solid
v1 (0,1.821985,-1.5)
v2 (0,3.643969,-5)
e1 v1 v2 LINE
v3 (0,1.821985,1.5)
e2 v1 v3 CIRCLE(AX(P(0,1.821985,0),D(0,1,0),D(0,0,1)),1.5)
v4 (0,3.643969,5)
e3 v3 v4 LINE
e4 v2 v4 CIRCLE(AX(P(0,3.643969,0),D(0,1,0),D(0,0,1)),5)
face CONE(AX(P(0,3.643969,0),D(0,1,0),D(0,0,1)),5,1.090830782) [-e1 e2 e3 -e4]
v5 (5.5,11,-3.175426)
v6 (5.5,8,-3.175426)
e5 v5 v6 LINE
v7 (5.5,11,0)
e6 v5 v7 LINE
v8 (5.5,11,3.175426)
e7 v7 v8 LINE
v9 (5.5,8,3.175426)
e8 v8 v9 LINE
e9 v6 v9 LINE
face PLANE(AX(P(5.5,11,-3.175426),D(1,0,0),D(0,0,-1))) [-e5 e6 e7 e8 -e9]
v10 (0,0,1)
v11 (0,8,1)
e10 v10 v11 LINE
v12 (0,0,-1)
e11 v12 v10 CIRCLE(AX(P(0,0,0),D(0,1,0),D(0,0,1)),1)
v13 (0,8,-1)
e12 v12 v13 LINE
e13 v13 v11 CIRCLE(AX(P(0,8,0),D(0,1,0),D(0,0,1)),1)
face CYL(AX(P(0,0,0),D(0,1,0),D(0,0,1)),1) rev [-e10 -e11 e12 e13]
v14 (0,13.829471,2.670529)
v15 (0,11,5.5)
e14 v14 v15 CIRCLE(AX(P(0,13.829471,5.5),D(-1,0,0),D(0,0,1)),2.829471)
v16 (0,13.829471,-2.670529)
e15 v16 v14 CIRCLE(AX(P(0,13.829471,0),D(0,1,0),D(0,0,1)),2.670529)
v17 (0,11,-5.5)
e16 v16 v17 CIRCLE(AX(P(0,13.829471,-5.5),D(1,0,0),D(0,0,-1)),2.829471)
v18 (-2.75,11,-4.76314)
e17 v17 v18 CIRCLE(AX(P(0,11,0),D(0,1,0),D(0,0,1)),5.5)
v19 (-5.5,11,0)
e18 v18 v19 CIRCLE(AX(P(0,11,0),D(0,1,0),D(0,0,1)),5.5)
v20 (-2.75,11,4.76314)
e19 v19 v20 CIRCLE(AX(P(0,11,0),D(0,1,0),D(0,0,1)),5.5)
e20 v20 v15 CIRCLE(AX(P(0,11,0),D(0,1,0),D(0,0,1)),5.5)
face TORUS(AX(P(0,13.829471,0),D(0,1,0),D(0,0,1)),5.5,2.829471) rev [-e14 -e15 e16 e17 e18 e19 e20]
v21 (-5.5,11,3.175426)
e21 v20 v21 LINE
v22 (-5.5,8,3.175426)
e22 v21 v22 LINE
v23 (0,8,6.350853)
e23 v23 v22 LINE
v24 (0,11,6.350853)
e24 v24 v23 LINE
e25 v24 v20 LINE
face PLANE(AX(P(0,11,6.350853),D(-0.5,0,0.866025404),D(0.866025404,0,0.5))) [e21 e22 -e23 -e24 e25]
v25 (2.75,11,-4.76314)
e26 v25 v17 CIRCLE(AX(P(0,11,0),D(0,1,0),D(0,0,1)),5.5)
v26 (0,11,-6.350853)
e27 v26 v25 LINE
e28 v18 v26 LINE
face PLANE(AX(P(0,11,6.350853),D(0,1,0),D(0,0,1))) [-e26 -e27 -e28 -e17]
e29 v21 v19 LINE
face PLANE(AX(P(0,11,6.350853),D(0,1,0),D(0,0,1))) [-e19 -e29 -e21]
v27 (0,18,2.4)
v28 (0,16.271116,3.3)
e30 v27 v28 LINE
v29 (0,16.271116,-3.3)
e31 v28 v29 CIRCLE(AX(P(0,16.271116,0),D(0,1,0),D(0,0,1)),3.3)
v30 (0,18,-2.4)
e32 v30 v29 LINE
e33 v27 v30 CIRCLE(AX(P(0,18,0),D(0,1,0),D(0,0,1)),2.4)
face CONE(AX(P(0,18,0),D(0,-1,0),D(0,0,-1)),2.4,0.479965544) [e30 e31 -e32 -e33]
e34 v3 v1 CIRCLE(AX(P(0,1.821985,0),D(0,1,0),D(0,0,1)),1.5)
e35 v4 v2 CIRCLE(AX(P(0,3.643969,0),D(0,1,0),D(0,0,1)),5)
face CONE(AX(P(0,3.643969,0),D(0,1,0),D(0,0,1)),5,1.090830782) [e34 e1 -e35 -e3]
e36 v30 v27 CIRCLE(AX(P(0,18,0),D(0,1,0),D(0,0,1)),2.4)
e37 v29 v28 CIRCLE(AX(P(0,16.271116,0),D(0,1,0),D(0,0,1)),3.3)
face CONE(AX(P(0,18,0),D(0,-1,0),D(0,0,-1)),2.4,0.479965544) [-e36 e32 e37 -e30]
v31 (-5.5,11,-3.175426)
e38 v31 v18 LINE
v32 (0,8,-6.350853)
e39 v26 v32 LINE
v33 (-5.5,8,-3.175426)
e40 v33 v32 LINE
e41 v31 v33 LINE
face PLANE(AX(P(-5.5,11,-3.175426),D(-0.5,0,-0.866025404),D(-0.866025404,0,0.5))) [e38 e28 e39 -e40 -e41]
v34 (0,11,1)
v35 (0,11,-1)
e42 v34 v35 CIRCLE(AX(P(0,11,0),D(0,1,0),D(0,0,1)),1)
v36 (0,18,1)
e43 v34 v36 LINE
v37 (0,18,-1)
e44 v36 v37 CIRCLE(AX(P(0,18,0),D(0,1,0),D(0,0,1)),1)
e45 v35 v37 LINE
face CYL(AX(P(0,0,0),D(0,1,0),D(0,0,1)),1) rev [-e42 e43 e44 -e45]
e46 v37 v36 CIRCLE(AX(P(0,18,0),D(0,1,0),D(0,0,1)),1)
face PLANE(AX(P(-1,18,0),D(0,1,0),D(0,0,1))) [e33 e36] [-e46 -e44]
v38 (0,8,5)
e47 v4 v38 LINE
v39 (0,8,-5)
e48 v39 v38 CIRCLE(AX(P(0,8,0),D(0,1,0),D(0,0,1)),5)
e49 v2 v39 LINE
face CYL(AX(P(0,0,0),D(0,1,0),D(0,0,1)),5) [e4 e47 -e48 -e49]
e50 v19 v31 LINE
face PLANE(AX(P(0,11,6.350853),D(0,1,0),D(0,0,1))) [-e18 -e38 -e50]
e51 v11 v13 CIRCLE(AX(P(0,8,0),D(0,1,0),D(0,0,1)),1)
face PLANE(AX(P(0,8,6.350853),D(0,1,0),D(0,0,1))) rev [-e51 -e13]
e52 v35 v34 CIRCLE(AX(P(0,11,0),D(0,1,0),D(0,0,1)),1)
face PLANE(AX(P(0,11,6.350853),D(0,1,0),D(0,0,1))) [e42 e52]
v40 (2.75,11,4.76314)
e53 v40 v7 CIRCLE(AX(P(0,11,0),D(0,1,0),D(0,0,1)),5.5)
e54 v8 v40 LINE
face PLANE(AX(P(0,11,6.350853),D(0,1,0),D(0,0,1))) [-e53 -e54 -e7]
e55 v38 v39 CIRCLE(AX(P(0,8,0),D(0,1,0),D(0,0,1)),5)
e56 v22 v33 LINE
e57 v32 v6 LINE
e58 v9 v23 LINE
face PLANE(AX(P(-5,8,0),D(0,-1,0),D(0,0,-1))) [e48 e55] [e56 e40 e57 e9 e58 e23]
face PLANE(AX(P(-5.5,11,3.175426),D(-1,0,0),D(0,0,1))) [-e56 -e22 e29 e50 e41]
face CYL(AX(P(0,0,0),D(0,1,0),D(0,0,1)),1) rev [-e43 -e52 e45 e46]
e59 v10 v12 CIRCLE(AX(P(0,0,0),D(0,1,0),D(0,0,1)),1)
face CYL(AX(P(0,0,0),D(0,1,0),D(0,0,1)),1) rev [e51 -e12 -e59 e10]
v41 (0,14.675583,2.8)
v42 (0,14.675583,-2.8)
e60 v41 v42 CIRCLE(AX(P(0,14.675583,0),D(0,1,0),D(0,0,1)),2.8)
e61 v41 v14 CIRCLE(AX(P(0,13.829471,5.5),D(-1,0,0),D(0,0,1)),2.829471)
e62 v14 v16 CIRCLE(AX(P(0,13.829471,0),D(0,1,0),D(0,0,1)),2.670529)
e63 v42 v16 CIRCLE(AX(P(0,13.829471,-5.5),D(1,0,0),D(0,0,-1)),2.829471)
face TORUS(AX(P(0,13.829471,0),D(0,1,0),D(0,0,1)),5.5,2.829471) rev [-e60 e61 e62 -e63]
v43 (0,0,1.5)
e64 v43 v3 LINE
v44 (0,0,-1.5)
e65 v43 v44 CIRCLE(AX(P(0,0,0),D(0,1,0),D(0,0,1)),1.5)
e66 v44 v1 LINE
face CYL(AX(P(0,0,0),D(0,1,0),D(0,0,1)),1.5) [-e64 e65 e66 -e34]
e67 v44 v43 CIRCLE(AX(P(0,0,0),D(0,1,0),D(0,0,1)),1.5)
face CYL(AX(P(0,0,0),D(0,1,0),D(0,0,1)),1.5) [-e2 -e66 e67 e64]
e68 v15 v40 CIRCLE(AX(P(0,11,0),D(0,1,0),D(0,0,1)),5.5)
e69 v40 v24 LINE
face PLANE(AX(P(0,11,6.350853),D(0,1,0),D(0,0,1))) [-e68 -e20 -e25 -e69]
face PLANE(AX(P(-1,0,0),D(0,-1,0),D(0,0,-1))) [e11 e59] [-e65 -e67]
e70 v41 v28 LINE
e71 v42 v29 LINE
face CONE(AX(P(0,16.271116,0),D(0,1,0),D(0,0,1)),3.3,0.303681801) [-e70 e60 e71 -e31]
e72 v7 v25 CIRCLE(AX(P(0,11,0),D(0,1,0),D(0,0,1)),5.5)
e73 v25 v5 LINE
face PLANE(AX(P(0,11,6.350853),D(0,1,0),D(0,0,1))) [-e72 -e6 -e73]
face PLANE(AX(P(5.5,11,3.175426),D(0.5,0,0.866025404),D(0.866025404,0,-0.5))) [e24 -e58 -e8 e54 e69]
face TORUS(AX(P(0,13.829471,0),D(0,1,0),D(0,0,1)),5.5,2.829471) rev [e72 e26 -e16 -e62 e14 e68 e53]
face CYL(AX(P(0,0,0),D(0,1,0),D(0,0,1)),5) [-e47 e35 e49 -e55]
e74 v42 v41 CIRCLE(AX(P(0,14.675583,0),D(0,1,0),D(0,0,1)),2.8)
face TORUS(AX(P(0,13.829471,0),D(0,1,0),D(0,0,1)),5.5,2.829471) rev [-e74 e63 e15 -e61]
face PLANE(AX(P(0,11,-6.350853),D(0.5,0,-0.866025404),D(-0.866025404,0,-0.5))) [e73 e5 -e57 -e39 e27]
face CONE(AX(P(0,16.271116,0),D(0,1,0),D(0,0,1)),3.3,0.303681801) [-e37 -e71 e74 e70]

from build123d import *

# Parameters (mm, degrees)
EXTRUDE_1_DEPTH = 3


with BuildPart() as part:
    # 草图1 → 旋转2 (revolve)
    with BuildSketch(Plane.XY, mode=Mode.PRIVATE) as revolve_2_sk:
        with BuildLine():
            Line((-1, 18), (-2.4, 18))
            Line((-2.4, 18), (-3.3, 16.271116086))
            Line((-3.3, 16.271116086), (-2.8, 14.675583457))
            ThreePointArc((-2.8, 14.675583457), (-3.219653878, 12.154380629), (-5.5, 11))
            Line((-5.5, 11), (-5.5, 8))
            Line((-5.5, 8), (-5, 8))
            Line((-5, 8), (-5, 3.643969354))
            Line((-5, 3.643969354), (-1.5, 1.821984677))
            Line((-1.5, 1.821984677), (-1.5, 0))
            Line((-1.5, 0), (-1, 0))
            Line((-1, 0), (-1, 18))
        make_face()
    revolve(revolve_2_sk.sketch.rotate(Axis((0, 0, 0), (0, -1, 0)), 270), axis=Axis((0, 0, 0), (0, -1, 0)))

    # 草图2 → 拉伸1 (add)
    with BuildSketch(Plane.XZ.offset(-8)):
        Polygon((-5.5, 3.175426481), (-5.5, -3.175426481), (0, -6.350852961), (5.5, -3.175426481), (5.5, 3.175426481), (0, 6.350852961), align=None)
    extrude(amount=-EXTRUDE_1_DEPTH)


solid = part.part
